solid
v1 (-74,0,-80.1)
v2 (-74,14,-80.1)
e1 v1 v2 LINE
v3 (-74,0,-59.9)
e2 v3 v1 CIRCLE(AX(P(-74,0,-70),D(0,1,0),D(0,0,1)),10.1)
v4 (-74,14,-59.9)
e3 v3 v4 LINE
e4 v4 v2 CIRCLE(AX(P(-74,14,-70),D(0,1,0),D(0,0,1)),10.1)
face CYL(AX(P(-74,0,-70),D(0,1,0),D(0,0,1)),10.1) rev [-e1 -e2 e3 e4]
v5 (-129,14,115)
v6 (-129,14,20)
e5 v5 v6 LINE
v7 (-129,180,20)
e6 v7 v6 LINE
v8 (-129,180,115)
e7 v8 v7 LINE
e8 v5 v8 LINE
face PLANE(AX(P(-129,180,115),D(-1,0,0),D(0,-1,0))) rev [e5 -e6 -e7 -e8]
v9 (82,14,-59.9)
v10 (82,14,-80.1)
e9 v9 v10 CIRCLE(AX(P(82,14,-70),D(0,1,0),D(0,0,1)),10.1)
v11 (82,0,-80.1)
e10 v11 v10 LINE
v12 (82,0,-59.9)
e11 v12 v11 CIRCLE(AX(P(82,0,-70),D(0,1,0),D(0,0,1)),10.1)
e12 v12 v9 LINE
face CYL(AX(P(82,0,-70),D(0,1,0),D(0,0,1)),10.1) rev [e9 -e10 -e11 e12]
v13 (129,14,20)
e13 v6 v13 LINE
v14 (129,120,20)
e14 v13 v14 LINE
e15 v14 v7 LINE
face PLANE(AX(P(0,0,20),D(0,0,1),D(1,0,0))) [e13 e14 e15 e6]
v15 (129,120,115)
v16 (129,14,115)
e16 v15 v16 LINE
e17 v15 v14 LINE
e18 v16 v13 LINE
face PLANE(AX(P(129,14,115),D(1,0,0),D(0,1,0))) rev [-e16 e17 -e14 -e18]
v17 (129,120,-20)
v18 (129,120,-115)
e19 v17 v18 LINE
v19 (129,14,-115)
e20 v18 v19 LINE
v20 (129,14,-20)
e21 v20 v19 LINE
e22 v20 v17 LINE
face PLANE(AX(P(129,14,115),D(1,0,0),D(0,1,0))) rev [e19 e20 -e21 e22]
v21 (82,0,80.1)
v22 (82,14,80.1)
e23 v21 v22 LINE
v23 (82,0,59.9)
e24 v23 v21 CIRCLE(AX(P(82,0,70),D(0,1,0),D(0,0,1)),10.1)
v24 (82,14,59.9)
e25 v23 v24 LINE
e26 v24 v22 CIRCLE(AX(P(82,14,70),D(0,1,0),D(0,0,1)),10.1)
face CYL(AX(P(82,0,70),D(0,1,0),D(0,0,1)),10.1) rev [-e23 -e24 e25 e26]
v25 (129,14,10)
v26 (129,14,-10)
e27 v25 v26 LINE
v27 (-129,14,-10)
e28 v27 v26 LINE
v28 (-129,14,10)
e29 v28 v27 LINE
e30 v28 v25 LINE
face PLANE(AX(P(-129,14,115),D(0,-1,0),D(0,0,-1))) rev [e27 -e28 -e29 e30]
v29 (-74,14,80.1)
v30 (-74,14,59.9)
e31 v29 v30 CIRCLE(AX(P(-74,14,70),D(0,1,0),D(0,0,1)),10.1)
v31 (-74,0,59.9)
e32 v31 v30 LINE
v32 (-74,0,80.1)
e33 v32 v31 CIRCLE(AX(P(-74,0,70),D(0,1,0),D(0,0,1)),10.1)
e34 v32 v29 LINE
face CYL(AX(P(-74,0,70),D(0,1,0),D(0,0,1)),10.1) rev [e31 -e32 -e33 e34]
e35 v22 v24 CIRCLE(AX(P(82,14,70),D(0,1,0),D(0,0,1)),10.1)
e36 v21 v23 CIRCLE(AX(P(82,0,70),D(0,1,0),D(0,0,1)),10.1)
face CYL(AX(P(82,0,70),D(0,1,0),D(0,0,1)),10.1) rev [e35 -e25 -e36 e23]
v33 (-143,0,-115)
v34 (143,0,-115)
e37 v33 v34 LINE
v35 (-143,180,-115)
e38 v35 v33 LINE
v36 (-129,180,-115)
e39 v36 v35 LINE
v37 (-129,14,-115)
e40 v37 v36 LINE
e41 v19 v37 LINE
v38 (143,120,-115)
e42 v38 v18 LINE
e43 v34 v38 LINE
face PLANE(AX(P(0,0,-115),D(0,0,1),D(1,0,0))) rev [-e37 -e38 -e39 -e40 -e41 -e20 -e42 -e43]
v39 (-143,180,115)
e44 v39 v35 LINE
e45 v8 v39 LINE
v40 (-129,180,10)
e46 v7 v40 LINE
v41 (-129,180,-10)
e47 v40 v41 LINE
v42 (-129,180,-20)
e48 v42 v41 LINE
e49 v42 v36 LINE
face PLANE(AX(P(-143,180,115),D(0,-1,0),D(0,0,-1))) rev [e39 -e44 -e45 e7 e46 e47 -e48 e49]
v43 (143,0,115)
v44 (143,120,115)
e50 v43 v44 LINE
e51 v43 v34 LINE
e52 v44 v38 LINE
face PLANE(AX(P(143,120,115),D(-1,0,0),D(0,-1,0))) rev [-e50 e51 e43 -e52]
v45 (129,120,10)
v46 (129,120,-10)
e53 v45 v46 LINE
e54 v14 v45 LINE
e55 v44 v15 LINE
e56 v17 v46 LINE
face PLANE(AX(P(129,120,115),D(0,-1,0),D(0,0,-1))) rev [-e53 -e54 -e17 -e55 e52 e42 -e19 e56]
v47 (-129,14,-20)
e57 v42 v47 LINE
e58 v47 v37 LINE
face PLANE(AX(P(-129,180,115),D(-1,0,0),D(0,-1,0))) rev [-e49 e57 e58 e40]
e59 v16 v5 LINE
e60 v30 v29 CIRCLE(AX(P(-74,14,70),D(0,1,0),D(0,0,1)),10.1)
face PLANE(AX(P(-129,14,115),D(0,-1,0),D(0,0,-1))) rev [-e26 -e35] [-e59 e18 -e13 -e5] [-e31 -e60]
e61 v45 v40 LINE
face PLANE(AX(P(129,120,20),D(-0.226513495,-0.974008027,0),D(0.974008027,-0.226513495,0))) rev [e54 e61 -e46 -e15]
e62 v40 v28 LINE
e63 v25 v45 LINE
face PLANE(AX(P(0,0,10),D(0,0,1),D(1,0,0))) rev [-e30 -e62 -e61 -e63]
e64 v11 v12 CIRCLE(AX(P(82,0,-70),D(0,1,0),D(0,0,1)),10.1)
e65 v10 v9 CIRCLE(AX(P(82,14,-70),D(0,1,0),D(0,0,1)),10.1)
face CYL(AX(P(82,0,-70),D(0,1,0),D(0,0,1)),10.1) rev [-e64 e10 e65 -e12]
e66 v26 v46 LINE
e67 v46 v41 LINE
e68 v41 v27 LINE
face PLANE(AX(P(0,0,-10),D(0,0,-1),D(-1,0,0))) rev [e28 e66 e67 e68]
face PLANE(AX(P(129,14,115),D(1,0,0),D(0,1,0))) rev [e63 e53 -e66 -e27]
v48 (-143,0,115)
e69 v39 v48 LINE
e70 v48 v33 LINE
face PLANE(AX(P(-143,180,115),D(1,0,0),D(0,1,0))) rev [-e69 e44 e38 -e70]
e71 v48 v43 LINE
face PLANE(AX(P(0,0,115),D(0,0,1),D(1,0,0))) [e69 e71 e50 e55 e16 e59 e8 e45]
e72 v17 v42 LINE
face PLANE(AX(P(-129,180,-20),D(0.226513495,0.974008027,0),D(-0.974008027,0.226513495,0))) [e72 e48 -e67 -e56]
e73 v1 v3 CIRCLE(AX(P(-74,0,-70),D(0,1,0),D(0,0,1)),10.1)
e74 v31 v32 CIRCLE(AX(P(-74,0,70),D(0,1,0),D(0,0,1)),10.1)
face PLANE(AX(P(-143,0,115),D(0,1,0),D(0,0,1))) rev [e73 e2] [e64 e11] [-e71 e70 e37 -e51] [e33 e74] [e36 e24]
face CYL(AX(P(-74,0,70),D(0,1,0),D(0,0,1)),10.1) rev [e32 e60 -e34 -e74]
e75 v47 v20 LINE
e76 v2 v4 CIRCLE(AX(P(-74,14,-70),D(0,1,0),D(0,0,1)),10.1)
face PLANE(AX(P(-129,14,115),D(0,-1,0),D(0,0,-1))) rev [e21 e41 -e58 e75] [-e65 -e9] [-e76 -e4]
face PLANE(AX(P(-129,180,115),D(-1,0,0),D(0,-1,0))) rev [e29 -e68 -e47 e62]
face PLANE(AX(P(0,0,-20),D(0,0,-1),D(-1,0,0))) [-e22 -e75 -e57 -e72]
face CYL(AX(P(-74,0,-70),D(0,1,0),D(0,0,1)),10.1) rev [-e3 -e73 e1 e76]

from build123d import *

# Parameters (mm, degrees)
EXTRUDE_1_DEPTH             = 115
EXTRUDE_START               = -10
EXTRUDE_2_DEPTH             = 10
EXTRUDE_START_2             = 10
EXTRUDE_3_DEPTH             = 10
SKETCH_4_R                  = 10.1
CUT_EXTRUDE_1_DEPTH         = 248.446964015
PATTERN_LINEAR_1_COUNT      = 2
PATTERN_LINEAR_1_PITCH      = 156
PATTERN_LINEAR_1_COUNT_DIR2 = 2
PATTERN_LINEAR_1_PITCH_DIR2 = 140


with BuildPart() as part:
    # 草图1 → 凸台-拉伸1 (new, symmetric)
    with BuildSketch(Plane.XY):
        Polygon((-143, 180), (-129, 180), (-129, 14), (129, 14), (129, 120), (143, 120), (143, 0), (-143, 0), align=None)
    extrude(amount=EXTRUDE_1_DEPTH, both=True)

    # 草图2 → 凸台-拉伸2 (add)
    with BuildSketch(Plane.XY.offset(EXTRUDE_START)):
        Polygon((129, 120), (129, 14), (-129, 14), (-129, 180), align=None)
    extrude(amount=-EXTRUDE_2_DEPTH)

    # 草图3 → 凸台-拉伸3 (add)
    with BuildSketch(Plane.XY.offset(EXTRUDE_START_2)):
        Polygon((-129, 180), (-129, 14), (129, 14), (129, 120), align=None)
    extrude(amount=EXTRUDE_3_DEPTH)

    # 草图4 → 切除-拉伸1 (cut, through all)
    with BuildSketch(Plane(origin=(0, 14, 0), x_dir=(1, 0, 0), z_dir=(0, 1, 0))):
        with Locations(Location((-74, -70, 0), (0, 0, 270))):
            Circle(SKETCH_4_R)
    cut_extrude_1 = extrude(amount=-CUT_EXTRUDE_1_DEPTH, mode=Mode.SUBTRACT)

    # 阵列(线性)1: Cut-Extrude 1 2 × 2
    with Locations(*[(i * PATTERN_LINEAR_1_PITCH, 0, -j * PATTERN_LINEAR_1_PITCH_DIR2) for i in range(PATTERN_LINEAR_1_COUNT) for j in range(PATTERN_LINEAR_1_COUNT_DIR2) if (i, j) != (0, 0)]):
        add(cut_extrude_1, mode=Mode.SUBTRACT)


solid = part.part
